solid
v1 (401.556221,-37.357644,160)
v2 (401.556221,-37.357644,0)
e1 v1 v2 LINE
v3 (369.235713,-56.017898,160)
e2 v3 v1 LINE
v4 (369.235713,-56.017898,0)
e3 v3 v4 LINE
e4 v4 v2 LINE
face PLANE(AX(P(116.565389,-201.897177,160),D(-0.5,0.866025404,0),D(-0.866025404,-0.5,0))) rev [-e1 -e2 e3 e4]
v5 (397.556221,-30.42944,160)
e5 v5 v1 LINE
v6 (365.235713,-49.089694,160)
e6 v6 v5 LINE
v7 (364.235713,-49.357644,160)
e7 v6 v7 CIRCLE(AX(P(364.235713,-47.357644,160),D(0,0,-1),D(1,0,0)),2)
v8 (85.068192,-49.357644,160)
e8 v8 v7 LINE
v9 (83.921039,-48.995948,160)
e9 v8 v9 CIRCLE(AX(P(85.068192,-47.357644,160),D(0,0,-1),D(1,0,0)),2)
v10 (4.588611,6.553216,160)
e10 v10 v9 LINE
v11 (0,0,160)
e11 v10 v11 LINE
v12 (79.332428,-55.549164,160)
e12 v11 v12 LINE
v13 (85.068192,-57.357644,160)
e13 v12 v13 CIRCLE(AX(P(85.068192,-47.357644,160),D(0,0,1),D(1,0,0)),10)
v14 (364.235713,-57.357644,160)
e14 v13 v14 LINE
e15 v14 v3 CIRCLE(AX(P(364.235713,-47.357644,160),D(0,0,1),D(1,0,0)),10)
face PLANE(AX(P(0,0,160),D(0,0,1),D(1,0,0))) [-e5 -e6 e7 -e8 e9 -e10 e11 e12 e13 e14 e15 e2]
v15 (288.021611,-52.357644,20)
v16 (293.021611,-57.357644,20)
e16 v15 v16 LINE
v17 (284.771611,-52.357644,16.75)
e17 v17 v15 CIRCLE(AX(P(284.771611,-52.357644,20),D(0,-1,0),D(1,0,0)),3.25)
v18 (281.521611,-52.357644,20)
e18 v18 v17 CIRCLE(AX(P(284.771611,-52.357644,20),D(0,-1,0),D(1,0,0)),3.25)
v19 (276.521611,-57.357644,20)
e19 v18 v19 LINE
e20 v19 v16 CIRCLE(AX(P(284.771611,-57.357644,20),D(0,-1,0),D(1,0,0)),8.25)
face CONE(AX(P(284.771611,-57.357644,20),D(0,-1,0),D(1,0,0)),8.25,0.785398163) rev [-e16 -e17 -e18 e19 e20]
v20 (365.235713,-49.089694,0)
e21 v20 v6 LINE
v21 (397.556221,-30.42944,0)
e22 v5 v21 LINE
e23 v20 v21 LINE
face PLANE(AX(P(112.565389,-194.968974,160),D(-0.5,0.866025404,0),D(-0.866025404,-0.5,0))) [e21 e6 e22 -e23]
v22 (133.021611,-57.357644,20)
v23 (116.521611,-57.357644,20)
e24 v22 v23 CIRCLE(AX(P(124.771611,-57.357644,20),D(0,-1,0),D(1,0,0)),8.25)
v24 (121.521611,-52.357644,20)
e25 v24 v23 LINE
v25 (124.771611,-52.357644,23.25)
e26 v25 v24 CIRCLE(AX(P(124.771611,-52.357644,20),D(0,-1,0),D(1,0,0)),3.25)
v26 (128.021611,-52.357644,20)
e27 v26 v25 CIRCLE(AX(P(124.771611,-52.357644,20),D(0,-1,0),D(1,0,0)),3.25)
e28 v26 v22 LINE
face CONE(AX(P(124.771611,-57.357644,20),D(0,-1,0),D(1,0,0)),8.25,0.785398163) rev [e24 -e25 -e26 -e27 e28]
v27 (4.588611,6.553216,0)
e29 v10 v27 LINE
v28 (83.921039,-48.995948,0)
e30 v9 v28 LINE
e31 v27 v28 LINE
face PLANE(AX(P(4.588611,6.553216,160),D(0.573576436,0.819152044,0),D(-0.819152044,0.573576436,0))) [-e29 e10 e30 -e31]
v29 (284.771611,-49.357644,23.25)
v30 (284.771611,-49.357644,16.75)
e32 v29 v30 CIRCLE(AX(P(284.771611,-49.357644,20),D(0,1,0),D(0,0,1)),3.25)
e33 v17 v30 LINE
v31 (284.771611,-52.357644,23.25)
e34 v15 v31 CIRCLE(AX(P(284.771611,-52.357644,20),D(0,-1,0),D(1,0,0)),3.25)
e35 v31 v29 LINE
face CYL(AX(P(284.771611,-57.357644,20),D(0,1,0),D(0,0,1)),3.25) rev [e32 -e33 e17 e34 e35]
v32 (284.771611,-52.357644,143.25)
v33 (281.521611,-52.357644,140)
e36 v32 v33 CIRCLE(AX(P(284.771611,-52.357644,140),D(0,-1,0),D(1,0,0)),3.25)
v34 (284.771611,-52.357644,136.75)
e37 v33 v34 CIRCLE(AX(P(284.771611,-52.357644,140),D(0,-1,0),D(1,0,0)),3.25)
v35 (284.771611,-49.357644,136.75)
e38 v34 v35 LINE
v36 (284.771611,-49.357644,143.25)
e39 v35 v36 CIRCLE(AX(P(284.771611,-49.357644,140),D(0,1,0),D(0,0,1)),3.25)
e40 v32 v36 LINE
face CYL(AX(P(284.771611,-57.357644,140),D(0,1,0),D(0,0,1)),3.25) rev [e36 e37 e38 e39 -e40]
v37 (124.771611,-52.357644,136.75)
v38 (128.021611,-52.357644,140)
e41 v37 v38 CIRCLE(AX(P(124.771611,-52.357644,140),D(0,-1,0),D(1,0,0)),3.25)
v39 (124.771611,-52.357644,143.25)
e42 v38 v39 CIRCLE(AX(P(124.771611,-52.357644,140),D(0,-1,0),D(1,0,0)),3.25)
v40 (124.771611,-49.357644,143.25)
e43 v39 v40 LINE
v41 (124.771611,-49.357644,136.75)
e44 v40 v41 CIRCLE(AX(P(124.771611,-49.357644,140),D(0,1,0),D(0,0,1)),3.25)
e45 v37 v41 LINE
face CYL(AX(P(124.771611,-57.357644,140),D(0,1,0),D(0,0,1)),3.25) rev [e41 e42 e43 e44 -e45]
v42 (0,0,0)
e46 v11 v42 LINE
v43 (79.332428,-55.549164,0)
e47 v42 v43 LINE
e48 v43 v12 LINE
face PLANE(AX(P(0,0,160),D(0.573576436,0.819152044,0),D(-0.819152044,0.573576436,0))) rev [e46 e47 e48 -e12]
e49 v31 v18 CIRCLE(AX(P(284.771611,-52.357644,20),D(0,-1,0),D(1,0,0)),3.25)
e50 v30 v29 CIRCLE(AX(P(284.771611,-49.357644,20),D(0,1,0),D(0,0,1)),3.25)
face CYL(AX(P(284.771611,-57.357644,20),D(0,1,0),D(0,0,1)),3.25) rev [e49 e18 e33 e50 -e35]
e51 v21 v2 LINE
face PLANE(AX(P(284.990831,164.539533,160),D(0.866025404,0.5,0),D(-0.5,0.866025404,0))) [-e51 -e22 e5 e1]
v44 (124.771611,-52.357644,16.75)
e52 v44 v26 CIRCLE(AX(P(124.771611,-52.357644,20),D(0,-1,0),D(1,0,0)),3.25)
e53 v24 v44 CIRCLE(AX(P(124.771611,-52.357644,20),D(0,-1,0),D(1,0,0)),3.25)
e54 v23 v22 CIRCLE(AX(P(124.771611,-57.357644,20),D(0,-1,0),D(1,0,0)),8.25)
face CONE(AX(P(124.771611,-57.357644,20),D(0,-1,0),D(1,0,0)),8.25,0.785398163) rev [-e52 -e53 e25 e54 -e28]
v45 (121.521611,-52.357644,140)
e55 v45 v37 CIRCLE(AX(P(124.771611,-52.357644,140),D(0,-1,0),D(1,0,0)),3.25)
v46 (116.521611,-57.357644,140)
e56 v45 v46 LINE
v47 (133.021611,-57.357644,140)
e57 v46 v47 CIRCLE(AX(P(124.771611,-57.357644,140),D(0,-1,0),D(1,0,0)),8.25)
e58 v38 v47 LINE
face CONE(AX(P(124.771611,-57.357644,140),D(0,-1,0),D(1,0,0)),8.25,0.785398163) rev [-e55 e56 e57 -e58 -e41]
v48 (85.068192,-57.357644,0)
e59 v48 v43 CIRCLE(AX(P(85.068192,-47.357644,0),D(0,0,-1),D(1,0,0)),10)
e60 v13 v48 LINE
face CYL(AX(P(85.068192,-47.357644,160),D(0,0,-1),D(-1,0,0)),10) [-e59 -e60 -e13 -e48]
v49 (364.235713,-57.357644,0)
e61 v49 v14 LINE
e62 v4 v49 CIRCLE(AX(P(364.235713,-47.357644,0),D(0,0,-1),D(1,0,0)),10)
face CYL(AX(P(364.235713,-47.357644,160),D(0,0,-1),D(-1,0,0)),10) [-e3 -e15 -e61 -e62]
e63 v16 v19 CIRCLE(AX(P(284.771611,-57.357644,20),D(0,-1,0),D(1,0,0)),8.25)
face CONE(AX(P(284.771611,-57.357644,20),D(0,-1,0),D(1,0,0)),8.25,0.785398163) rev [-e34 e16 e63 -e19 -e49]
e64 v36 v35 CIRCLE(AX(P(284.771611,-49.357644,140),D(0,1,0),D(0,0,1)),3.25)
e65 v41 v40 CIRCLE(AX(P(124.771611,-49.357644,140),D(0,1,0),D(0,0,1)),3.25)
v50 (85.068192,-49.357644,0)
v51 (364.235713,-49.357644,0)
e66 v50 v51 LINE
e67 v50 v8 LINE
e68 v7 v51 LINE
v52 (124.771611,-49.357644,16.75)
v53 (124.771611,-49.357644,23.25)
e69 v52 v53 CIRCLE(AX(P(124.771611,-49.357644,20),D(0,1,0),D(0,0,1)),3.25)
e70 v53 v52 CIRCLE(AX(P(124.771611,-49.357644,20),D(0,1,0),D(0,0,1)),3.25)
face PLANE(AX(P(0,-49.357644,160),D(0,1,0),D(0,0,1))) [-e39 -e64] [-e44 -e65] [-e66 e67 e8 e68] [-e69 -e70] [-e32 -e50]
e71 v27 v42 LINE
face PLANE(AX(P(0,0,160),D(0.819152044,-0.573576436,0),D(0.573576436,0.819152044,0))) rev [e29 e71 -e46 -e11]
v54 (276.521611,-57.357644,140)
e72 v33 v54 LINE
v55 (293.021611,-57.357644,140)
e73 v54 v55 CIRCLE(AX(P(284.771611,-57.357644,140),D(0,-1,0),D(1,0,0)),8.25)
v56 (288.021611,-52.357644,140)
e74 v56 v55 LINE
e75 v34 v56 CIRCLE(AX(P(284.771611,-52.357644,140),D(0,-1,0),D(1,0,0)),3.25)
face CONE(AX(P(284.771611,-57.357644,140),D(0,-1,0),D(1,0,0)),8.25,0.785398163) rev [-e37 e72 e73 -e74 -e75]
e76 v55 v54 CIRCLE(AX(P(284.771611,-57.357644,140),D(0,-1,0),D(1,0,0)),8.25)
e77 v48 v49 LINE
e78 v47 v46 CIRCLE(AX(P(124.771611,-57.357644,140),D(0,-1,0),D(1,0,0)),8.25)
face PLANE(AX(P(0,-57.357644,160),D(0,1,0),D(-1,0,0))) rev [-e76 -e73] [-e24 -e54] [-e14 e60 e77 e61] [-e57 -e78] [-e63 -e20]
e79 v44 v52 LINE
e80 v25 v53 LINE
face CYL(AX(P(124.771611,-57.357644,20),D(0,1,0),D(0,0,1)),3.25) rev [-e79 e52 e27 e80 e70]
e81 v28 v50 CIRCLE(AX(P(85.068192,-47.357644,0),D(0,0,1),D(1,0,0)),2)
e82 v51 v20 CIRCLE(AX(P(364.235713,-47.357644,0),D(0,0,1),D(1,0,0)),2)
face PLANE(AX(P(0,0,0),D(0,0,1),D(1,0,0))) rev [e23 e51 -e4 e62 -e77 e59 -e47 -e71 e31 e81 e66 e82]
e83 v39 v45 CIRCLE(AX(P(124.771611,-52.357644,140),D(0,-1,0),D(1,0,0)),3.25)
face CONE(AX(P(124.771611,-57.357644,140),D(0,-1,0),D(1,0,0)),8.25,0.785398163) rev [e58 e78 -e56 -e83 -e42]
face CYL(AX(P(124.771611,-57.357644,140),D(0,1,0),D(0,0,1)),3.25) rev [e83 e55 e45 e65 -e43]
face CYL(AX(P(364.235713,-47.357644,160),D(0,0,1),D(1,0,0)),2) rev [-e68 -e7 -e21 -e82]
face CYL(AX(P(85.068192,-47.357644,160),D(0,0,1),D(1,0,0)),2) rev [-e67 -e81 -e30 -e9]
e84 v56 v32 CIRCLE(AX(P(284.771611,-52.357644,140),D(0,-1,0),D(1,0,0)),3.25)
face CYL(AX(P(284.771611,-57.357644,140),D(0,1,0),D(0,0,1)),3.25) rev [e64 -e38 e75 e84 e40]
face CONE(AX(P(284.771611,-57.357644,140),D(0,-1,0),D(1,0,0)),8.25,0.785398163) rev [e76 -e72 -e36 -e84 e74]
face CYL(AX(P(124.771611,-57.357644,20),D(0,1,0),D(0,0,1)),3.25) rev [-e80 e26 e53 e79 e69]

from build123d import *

# Parameters (mm, degrees)
BOSS_EXTRUDE4_DEPTH          = 160
SKETCH24_R                   = 3.25
CUT_EXTRUDE3_DEPTH           = 8
SKETCH26_R                   = 8.25
CUT_EXTRUDE4_DEPTH           = 5
CUT_EXTRUDE4_DRAFT           = -45
CUT_EXTRUDE4_PROFILE_2_DEPTH = 5
CUT_EXTRUDE4_PROFILE_2_DRAFT = -45
CUT_EXTRUDE4_PROFILE_3_DEPTH = 5
CUT_EXTRUDE4_PROFILE_3_DRAFT = -45
CUT_EXTRUDE4_PROFILE_4_DEPTH = 5
CUT_EXTRUDE4_PROFILE_4_DRAFT = -45
FILLET1_R                    = 10
FILLET2_R                    = 2


with BuildPart() as part:
    # Sketch23 → Boss-Extrude4 (new body)
    with BuildSketch(Plane.XY):
        Polygon((4.588611491, 6.553216354), (0, 0), (81.915204429, -57.357643635), (366.915204429, -57.357643635), (401.55622058, -37.357643635), (397.55622058, -30.429440405), (364.771610889, -49.357643635), (84.43759474, -49.357643635), align=None)
    extrude(amount=BOSS_EXTRUDE4_DEPTH)

    # Sketch24 → Cut-Extrude3 (cut)
    with BuildSketch(Plane(origin=(0, -49.357643635, 0), x_dir=(1, 0, 0), z_dir=(0, 1, 0))):
        with Locations(Location((124.771610889, -20, 0), (0, 0, 270))):
            Circle(SKETCH24_R)
        with Locations(Location((284.771610889, -20, 0), (0, 0, 270))):
            Circle(SKETCH24_R)
        with Locations(Location((124.771610889, -140, 0), (0, 0, 270))):
            Circle(SKETCH24_R)
        with Locations(Location((284.771610889, -140, 0), (0, 0, 270))):
            Circle(SKETCH24_R)
    extrude(amount=-CUT_EXTRUDE3_DEPTH, mode=Mode.SUBTRACT)


with BuildPart() as cut_extrude4_tool:
    # Sketch26 → Cut-Extrude4 (with draft: the straight prism first)
    with BuildSketch(Plane.XZ.offset(57.357643635)):
        with Locations((124.771610889, 140)):
            Circle(SKETCH26_R)
    extrude(amount=-CUT_EXTRUDE4_DEPTH)
    # Cut-Extrude4: the draft: its side faces are tilted about the plane it starts from
    cut_extrude4_sides = [cut_extrude4_tool.faces().sort_by_distance(p)[0] for p in [
        (116.521610889, -54.857643635, 140),
    ]]
    draft(cut_extrude4_sides, Plane.XZ.offset(57.357643635), CUT_EXTRUDE4_DRAFT)


with BuildPart() as part_1:
    add(part.part)

    # Cut-Extrude4: cut by cut_extrude4_tool
    add(cut_extrude4_tool.part, mode=Mode.SUBTRACT)


with BuildPart() as cut_extrude4_profile_2_tool:
    # Sketch26 → Cut-Extrude4 profile 2 (with draft: the straight prism first)
    with BuildSketch(Plane.XZ.offset(57.357643635)):
        with Locations((284.771610889, 140)):
            Circle(SKETCH26_R)
    extrude(amount=-CUT_EXTRUDE4_PROFILE_2_DEPTH)
    # Cut-Extrude4 profile 2: the draft: its side faces are tilted about the plane it starts from
    cut_extrude4_profile_2_sides = [cut_extrude4_profile_2_tool.faces().sort_by_distance(p)[0] for p in [
        (276.521610889, -54.857643635, 140),
    ]]
    draft(cut_extrude4_profile_2_sides, Plane.XZ.offset(57.357643635), CUT_EXTRUDE4_PROFILE_2_DRAFT)


with BuildPart() as part_2:
    add(part_1.part)

    # Cut-Extrude4 profile 2: cut by cut_extrude4_profile_2_tool
    add(cut_extrude4_profile_2_tool.part, mode=Mode.SUBTRACT)


with BuildPart() as cut_extrude4_profile_3_tool:
    # Sketch26 → Cut-Extrude4 profile 3 (with draft: the straight prism first)
    with BuildSketch(Plane.XZ.offset(57.357643635)):
        with Locations((284.771610889, 20)):
            Circle(SKETCH26_R)
    extrude(amount=-CUT_EXTRUDE4_PROFILE_3_DEPTH)
    # Cut-Extrude4 profile 3: the draft: its side faces are tilted about the plane it starts from
    cut_extrude4_profile_3_sides = [cut_extrude4_profile_3_tool.faces().sort_by_distance(p)[0] for p in [
        (276.521610889, -54.857643635, 20),
    ]]
    draft(cut_extrude4_profile_3_sides, Plane.XZ.offset(57.357643635), CUT_EXTRUDE4_PROFILE_3_DRAFT)


with BuildPart() as part_3:
    add(part_2.part)

    # Cut-Extrude4 profile 3: cut by cut_extrude4_profile_3_tool
    add(cut_extrude4_profile_3_tool.part, mode=Mode.SUBTRACT)


with BuildPart() as cut_extrude4_profile_4_tool:
    # Sketch26 → Cut-Extrude4 profile 4 (with draft: the straight prism first)
    with BuildSketch(Plane.XZ.offset(57.357643635)):
        with Locations((124.771610889, 20)):
            Circle(SKETCH26_R)
    extrude(amount=-CUT_EXTRUDE4_PROFILE_4_DEPTH)
    # Cut-Extrude4 profile 4: the draft: its side faces are tilted about the plane it starts from
    cut_extrude4_profile_4_sides = [cut_extrude4_profile_4_tool.faces().sort_by_distance(p)[0] for p in [
        (116.521610889, -54.857643635, 20),
    ]]
    draft(cut_extrude4_profile_4_sides, Plane.XZ.offset(57.357643635), CUT_EXTRUDE4_PROFILE_4_DRAFT)


with BuildPart() as part_4:
    add(part_3.part)

    # Cut-Extrude4 profile 4: cut by cut_extrude4_profile_4_tool
    add(cut_extrude4_profile_4_tool.part, mode=Mode.SUBTRACT)

    # Fillet1
    fillet1_edges = [part_4.edges().sort_by_distance(p)[0] for p in [
        (366.915204429, -57.357643635, 80),
        (81.915204429, -57.357643635, 80),
    ]]
    fillet(fillet1_edges, radius=FILLET1_R)

    # Fillet2
    fillet2_edges = [part_4.edges().sort_by_distance(p)[0] for p in [
        (84.43759474, -49.357643635, 80),
        (364.771610889, -49.357643635, 80),
    ]]
    fillet(fillet2_edges, radius=FILLET2_R)


solid = part_4.part
